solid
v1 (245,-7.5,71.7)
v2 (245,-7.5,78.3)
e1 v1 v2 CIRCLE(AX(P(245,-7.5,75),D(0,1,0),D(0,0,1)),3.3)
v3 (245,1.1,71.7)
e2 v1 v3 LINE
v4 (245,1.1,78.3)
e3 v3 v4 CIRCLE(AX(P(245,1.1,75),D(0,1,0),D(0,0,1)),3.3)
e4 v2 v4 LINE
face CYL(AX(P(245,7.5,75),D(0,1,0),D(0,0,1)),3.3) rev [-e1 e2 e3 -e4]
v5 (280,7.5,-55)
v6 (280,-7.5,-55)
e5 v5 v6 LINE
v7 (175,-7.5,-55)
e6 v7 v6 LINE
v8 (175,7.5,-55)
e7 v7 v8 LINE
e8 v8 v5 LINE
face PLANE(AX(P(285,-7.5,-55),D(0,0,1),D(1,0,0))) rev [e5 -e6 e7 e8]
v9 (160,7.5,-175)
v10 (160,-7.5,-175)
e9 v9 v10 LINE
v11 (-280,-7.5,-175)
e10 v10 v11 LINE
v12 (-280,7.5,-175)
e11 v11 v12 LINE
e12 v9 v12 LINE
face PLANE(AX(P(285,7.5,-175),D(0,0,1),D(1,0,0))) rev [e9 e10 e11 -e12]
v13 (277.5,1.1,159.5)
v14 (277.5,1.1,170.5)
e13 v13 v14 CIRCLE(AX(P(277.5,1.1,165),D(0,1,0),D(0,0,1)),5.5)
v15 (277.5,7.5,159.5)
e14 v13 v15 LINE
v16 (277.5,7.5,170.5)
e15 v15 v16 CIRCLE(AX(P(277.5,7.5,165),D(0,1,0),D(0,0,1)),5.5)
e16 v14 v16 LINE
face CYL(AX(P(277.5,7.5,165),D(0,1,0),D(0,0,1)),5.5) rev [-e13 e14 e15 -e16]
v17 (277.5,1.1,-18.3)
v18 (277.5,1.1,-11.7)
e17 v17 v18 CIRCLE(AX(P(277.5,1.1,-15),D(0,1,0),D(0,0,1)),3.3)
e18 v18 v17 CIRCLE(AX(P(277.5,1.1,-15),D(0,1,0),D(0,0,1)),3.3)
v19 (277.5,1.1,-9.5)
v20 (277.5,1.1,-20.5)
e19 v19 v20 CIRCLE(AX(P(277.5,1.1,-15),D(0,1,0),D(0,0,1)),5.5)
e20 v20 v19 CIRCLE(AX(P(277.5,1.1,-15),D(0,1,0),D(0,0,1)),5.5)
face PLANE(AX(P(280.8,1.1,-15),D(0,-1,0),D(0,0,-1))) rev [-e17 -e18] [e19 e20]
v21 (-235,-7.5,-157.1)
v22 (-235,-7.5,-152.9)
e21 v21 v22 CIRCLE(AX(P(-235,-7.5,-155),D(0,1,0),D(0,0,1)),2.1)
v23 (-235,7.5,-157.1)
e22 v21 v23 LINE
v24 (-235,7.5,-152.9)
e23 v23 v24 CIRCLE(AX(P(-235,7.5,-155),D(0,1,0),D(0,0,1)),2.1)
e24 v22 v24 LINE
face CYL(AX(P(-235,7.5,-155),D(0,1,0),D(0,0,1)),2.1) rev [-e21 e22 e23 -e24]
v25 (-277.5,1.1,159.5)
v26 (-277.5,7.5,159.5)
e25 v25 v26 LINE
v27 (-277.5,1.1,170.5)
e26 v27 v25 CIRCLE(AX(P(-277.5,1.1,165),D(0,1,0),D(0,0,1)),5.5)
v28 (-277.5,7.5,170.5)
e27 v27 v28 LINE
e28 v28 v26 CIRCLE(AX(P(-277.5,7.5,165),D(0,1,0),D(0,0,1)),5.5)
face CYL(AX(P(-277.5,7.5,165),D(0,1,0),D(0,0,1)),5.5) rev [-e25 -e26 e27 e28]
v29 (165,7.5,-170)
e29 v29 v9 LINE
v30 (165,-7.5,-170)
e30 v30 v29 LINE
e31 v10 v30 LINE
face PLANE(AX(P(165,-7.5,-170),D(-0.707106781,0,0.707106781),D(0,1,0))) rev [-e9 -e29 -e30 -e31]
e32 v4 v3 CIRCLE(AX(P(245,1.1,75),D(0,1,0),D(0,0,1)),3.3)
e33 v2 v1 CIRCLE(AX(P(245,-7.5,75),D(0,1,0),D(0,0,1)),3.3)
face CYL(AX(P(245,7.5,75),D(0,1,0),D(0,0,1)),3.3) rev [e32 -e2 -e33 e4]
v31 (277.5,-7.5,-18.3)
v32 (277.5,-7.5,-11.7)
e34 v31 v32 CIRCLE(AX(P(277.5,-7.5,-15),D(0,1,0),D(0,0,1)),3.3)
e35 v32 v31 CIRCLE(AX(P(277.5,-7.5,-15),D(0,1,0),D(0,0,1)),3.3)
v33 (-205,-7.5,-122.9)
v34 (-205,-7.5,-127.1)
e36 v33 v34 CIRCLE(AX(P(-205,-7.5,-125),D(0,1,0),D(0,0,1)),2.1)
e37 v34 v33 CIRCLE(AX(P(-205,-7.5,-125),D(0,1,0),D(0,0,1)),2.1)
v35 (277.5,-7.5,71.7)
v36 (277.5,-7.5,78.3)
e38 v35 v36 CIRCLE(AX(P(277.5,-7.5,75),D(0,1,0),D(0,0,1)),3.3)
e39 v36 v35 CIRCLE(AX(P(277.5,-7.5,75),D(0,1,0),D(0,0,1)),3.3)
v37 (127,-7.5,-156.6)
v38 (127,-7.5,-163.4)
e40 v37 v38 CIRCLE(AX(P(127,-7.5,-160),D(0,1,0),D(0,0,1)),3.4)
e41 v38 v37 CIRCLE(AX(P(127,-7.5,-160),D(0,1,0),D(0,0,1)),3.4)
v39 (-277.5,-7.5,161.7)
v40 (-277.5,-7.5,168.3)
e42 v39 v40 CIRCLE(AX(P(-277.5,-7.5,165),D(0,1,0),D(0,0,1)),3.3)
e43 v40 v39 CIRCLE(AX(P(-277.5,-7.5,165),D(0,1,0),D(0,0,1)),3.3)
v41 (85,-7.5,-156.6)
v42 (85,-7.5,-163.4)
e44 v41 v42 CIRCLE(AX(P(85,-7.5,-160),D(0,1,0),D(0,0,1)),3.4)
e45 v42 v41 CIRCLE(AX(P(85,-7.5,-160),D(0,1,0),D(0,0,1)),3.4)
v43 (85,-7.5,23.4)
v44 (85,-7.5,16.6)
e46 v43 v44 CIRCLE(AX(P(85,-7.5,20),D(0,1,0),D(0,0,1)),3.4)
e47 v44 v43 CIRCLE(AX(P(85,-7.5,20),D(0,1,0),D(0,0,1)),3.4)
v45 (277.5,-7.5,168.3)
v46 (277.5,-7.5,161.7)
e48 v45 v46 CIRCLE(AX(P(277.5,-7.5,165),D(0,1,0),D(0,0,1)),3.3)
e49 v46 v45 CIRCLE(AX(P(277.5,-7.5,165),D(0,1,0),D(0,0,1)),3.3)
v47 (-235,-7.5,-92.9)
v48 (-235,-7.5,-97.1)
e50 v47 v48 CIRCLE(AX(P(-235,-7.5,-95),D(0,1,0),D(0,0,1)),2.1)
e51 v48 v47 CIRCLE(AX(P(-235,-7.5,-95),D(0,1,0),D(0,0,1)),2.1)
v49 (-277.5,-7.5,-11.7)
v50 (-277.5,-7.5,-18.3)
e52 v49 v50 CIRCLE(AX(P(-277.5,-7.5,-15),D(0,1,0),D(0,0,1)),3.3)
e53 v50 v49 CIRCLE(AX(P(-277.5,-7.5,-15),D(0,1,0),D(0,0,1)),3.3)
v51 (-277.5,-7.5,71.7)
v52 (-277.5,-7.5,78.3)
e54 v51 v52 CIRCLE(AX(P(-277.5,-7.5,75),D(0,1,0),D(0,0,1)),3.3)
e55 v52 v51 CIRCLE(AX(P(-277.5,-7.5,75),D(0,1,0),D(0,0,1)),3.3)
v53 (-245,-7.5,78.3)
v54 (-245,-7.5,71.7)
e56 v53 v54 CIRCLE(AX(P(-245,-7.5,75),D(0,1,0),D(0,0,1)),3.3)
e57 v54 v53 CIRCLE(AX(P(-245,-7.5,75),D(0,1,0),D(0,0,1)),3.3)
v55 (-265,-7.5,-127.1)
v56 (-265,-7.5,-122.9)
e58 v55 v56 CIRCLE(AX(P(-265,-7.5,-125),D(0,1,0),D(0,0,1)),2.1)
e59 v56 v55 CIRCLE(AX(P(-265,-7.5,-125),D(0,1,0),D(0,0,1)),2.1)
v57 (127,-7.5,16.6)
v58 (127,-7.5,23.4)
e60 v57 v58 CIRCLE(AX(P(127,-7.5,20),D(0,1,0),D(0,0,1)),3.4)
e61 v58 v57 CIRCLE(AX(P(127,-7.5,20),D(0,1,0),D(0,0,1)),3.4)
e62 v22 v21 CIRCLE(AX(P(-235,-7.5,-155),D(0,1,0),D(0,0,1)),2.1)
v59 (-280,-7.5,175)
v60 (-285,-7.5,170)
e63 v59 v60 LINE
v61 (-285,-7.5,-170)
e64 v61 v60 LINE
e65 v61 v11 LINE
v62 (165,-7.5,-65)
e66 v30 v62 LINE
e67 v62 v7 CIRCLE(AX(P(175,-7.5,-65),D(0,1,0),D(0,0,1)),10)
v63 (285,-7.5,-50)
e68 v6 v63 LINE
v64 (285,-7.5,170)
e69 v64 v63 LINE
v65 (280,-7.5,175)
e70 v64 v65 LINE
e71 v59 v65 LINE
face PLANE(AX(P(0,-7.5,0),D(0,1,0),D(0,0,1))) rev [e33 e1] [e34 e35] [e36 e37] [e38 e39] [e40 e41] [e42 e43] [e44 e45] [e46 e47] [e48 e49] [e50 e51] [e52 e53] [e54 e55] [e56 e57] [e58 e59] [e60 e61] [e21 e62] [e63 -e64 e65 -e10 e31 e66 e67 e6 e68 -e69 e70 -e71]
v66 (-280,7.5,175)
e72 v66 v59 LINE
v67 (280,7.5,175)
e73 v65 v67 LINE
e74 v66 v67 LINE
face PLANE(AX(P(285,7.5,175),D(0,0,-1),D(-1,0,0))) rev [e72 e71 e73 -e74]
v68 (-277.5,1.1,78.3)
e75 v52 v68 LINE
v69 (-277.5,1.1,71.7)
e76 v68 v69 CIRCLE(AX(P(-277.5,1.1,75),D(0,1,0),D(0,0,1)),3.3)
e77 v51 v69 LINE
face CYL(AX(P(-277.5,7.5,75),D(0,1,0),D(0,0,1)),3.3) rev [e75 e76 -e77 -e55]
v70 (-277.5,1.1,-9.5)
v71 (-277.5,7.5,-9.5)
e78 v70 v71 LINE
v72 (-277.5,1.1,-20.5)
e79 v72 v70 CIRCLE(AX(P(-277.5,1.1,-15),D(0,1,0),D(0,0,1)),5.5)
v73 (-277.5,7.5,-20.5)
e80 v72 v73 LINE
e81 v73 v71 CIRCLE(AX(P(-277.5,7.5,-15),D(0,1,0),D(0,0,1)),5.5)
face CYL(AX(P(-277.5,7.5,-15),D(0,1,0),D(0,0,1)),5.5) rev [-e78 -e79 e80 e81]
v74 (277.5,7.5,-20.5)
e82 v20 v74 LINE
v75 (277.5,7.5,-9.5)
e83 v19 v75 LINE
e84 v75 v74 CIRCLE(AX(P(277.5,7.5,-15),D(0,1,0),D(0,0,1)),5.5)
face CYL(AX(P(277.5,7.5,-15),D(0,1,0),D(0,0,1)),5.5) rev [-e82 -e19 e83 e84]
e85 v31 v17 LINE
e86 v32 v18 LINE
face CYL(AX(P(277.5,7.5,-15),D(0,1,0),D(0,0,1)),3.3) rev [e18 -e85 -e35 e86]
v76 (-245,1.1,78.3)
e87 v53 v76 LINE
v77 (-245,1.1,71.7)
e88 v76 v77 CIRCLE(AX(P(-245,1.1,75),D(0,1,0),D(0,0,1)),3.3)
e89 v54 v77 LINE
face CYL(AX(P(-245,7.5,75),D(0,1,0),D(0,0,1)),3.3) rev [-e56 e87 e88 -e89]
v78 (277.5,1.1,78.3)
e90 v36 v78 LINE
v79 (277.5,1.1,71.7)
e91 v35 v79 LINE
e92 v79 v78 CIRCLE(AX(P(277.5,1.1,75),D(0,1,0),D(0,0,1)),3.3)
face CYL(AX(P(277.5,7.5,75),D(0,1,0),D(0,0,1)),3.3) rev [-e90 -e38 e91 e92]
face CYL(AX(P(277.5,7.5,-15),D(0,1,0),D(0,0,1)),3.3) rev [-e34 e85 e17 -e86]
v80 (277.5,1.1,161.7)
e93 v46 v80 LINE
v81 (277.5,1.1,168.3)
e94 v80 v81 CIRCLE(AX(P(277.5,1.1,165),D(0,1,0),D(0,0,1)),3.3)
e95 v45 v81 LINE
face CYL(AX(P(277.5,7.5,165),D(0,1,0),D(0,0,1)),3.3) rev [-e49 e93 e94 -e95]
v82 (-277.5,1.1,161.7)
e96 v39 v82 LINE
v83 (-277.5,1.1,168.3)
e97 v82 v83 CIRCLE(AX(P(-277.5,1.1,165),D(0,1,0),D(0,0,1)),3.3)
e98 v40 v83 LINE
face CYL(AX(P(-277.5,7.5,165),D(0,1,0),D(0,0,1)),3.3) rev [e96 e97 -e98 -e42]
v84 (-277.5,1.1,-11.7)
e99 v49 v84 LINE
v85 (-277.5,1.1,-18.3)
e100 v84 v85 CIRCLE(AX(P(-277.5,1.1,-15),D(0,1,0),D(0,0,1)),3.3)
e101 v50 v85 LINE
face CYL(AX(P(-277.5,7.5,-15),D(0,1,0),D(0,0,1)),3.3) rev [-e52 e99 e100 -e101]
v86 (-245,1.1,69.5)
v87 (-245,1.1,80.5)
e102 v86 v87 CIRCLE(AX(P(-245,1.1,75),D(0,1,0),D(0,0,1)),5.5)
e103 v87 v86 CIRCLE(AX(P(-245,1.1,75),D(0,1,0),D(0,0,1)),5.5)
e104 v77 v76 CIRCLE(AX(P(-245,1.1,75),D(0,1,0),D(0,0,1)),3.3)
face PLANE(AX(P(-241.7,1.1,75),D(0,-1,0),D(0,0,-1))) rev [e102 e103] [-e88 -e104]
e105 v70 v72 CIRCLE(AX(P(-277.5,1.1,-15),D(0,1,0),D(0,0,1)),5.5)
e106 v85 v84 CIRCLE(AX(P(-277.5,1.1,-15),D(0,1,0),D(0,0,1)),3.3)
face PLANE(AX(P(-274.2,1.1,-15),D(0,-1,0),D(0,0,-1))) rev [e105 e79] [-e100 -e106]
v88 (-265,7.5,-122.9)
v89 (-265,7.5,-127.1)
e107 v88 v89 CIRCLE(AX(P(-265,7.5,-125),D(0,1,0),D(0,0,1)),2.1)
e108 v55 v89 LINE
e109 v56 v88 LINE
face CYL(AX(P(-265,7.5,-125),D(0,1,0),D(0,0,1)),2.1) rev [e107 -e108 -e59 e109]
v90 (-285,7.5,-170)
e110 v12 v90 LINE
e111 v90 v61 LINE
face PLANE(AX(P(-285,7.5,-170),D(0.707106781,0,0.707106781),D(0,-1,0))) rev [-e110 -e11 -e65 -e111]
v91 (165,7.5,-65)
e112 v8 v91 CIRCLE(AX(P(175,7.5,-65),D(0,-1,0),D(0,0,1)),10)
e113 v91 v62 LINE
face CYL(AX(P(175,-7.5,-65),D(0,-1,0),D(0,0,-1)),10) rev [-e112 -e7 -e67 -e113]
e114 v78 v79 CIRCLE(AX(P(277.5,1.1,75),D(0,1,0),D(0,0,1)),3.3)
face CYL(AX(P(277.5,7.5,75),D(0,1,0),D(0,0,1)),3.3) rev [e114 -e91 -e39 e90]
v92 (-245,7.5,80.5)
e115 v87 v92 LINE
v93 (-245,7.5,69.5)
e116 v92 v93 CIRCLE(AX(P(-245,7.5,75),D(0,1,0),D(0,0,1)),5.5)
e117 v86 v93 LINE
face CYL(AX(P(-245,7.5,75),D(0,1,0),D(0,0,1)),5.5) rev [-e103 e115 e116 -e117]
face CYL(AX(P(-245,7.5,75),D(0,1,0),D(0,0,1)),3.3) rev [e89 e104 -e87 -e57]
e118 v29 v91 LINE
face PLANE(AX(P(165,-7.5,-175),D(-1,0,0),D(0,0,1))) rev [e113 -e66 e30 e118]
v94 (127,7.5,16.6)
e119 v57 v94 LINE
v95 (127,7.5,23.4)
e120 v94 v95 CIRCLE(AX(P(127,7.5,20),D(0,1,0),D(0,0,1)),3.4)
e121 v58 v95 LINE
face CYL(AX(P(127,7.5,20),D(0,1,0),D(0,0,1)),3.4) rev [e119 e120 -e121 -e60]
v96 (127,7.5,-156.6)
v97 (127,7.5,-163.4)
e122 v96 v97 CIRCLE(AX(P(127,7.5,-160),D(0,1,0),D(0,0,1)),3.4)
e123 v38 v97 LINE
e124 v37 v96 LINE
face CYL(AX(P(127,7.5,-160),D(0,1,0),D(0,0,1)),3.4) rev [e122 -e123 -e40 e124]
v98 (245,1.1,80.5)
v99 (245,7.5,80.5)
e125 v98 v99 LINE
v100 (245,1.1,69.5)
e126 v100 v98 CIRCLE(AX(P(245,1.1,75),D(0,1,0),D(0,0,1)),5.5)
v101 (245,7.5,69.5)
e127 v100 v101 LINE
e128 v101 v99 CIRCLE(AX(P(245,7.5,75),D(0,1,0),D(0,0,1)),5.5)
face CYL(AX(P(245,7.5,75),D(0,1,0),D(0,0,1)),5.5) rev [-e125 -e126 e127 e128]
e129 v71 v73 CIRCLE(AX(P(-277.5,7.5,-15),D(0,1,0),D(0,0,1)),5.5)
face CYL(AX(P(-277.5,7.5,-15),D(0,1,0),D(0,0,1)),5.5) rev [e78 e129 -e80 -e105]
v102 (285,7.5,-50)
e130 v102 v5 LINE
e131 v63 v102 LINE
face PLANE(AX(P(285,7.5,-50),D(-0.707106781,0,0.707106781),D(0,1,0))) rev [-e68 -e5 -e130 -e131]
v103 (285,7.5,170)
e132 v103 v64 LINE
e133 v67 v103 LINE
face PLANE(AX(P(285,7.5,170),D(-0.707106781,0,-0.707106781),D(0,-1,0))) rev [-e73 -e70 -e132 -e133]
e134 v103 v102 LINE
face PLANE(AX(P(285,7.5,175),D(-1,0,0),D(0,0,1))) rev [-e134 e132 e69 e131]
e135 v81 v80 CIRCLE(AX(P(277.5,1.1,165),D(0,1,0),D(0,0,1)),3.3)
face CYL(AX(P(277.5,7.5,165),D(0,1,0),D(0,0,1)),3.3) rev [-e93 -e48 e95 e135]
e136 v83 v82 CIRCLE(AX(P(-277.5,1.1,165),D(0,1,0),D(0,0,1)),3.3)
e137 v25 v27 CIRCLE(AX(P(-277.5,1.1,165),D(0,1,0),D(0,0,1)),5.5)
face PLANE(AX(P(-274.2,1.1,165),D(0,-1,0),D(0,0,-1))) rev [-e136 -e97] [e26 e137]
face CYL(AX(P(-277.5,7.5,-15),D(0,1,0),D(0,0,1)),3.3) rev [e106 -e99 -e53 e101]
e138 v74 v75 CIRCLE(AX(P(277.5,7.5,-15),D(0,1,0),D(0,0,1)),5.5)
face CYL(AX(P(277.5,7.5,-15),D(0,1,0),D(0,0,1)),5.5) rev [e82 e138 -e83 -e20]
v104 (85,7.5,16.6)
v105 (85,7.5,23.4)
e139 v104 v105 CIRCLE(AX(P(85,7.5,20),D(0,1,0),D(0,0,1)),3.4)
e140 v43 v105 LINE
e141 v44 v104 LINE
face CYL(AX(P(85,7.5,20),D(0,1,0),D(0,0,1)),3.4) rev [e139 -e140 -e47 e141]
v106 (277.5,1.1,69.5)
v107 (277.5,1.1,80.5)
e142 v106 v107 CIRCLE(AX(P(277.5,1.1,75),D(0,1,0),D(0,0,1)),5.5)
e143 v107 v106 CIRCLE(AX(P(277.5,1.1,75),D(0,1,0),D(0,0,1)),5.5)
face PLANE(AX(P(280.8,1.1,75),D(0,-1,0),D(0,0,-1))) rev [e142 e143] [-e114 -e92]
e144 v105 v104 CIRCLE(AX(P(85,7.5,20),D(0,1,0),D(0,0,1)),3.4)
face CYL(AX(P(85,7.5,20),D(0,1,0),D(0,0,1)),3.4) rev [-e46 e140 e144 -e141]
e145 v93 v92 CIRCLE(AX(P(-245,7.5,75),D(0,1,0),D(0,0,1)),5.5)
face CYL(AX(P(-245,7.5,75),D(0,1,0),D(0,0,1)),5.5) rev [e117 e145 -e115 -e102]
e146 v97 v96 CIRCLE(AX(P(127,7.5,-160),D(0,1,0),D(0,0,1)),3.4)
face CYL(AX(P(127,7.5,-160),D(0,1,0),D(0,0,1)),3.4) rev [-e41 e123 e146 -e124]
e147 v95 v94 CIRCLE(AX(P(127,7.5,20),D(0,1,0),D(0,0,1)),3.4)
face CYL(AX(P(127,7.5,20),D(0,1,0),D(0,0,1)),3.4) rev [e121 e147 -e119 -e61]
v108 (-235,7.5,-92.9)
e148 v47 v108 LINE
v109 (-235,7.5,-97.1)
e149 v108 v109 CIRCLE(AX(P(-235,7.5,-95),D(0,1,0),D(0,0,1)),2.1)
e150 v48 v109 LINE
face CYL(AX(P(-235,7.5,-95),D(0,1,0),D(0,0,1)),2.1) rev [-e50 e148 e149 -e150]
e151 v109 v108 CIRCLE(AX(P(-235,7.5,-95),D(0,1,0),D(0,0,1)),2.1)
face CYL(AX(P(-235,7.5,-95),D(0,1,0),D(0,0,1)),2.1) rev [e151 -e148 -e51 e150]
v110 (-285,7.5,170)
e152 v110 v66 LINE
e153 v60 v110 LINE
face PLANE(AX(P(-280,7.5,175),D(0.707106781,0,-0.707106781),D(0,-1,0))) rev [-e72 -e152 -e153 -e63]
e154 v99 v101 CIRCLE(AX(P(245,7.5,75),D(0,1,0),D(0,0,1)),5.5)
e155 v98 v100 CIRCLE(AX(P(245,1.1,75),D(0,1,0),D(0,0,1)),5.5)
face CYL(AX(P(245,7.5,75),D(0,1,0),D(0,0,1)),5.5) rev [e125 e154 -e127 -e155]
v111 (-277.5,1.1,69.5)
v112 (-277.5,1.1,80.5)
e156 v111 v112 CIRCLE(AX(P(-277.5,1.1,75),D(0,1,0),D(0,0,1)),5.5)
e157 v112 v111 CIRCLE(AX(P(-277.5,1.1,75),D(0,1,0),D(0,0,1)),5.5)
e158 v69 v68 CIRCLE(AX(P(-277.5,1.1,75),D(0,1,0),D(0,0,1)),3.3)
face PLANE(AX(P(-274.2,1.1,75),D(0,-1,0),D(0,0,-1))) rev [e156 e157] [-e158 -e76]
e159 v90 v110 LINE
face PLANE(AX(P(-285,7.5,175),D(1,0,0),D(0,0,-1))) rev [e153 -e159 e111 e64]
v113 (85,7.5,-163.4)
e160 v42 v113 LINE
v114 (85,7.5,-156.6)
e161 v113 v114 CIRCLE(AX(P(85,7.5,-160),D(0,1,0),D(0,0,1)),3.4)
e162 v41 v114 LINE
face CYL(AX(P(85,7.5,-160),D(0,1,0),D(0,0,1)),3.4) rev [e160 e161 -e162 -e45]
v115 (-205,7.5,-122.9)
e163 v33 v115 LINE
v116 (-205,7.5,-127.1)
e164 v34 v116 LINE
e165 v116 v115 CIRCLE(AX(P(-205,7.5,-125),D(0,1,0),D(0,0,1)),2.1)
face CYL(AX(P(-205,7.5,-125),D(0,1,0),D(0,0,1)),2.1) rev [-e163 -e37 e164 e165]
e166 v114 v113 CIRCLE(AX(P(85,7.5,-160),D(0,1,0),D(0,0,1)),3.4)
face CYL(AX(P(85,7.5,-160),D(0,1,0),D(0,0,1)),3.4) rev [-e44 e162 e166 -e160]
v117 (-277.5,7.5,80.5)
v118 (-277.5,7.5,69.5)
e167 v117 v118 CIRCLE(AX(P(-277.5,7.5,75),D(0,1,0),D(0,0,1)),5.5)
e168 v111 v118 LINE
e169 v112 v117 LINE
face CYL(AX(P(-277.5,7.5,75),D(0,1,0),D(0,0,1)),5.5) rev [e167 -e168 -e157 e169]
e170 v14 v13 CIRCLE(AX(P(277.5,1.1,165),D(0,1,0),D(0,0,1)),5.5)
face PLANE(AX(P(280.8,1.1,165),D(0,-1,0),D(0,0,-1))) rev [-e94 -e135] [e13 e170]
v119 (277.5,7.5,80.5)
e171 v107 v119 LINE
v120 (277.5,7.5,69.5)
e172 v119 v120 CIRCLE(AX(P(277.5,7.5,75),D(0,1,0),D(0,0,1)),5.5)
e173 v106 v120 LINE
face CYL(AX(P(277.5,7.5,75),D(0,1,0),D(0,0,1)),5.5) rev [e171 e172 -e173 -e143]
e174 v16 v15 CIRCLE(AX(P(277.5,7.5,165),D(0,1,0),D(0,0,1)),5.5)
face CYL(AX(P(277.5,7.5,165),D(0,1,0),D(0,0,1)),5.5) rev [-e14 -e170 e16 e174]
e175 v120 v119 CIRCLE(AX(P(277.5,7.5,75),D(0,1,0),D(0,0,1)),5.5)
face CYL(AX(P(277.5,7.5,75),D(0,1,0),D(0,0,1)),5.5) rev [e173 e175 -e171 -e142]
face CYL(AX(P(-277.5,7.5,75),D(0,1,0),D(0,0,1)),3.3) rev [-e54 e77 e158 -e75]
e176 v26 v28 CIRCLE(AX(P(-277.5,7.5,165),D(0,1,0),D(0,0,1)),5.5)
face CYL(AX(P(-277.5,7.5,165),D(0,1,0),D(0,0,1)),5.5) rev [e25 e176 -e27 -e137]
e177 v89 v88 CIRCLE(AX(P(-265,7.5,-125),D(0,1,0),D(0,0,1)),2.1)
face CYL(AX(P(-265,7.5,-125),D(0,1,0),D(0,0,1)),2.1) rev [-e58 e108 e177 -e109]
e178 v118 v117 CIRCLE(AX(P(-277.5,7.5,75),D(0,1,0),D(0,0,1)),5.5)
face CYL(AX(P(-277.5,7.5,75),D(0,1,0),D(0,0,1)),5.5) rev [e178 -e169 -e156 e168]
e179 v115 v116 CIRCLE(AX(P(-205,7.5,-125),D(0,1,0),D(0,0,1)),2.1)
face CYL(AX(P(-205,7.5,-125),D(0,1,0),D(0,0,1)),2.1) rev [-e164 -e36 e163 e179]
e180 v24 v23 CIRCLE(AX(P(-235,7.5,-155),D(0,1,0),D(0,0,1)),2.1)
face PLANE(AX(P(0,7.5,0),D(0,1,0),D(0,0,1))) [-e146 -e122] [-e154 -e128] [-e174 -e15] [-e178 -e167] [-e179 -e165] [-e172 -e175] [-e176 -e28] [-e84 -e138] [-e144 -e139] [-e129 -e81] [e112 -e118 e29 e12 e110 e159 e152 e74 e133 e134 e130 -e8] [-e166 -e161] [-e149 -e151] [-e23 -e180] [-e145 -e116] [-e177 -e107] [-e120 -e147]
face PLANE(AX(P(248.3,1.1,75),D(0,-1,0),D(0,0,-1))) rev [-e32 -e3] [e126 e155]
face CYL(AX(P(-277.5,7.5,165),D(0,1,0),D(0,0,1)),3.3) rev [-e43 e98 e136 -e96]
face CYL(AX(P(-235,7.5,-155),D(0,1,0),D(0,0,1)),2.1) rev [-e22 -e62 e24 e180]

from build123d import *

# Parameters (mm, degrees)
SKETCH_1_W                   = 570
SKETCH_1_H                   = 350
EXTRUDE_1_DEPTH              = 7.5
CHAMFER_1_SIZE               = 5
HOLE_WIZARD_M5_1_D           = 4.2
HOLE_WIZARD_M8_1_D           = 6.8
HOLE_WIZARD_M6_1_D           = 6.6
HOLE_WIZARD_M6_1_DEPTH       = 17
HOLE_WIZARD_M6_1_CBORE_D     = 11
HOLE_WIZARD_M6_1_CBORE_DEPTH = 6.4
HOLE_WIZARD_M6_1_TIP         = 1.982840043
HOLE_WIZARD_M6_2_D           = 6.6
HOLE_WIZARD_M6_2_DEPTH       = 17
HOLE_WIZARD_M6_2_CBORE_D     = 11
HOLE_WIZARD_M6_2_CBORE_DEPTH = 6.4
HOLE_WIZARD_M6_2_TIP         = 1.982840043
SKETCH_10_W                  = 120
SKETCH_10_H                  = 120
CUT_EXTRUDE_1_DEPTH          = 335.776044543
FILLET_1_R                   = 10
CHAMFER_2_SIZE               = 5


with BuildPart() as part:
    # 草图1 → 凸台-拉伸1 (new, symmetric)
    with BuildSketch(Plane(origin=(0, 0, 0), x_dir=(1, 0, 0), z_dir=(0, 1, 0))):
        Rectangle(SKETCH_1_W, SKETCH_1_H)
    extrude(amount=EXTRUDE_1_DEPTH, both=True)

    # 倒角1
    chamfer_1_edges = [part.edges().sort_by_distance(p)[0] for p in [
        (-285, 0, -175),
        (285, 0, -175),
        (285, 0, 175),
        (-285, 0, 175),
    ]]
    chamfer(chamfer_1_edges, length=CHAMFER_1_SIZE)

    # M5 螺纹孔1 (through all)
    with Locations(Plane(origin=(0, 7.5, 0), x_dir=(1, 0, 0), z_dir=(0, 1, 0))):
        with Locations((-265, 125), (-235, 95), (-235, 155), (-205, 125)):
            Hole(HOLE_WIZARD_M5_1_D / 2)

    # M8 螺纹孔1 (through all)
    with Locations(Plane(origin=(0, 7.5, 0), x_dir=(1, 0, 0), z_dir=(0, 1, 0))):
        with Locations((85, -20), (127, -20), (127, 160), (85, 160)):
            Hole(HOLE_WIZARD_M8_1_D / 2)

    # M6 六角凹头螺钉的柱形沉头孔1
    with Locations(Plane(origin=(0, 7.5, 0), x_dir=(1, 0, 0), z_dir=(0, 1, 0))):
        with Locations((-277.5, 15), (-277.5, -165), (277.5, 15), (277.5, -165), (-277.5, -75), (277.5, -75)):
            CounterBoreHole(HOLE_WIZARD_M6_1_D / 2, HOLE_WIZARD_M6_1_CBORE_D / 2, HOLE_WIZARD_M6_1_CBORE_DEPTH, depth=HOLE_WIZARD_M6_1_DEPTH)
            with Locations((0, 0, -(HOLE_WIZARD_M6_1_DEPTH + HOLE_WIZARD_M6_1_TIP / 2))):  # 118° drill point
                Cone(0, HOLE_WIZARD_M6_1_D / 2, HOLE_WIZARD_M6_1_TIP, mode=Mode.SUBTRACT)

    # M6 六角凹头螺钉的柱形沉头孔2
    with Locations(Plane(origin=(0, 7.5, 0), x_dir=(1, 0, 0), z_dir=(0, 1, 0))):
        with Locations((-245, -75), (245, -75)):
            CounterBoreHole(HOLE_WIZARD_M6_2_D / 2, HOLE_WIZARD_M6_2_CBORE_D / 2, HOLE_WIZARD_M6_2_CBORE_DEPTH, depth=HOLE_WIZARD_M6_2_DEPTH)
            with Locations((0, 0, -(HOLE_WIZARD_M6_2_DEPTH + HOLE_WIZARD_M6_2_TIP / 2))):  # 118° drill point
                Cone(0, HOLE_WIZARD_M6_2_D / 2, HOLE_WIZARD_M6_2_TIP, mode=Mode.SUBTRACT)

    # 草图10 → 切除-拉伸1 (cut, through all)
    with BuildSketch(Plane(origin=(0, 7.5, 0), x_dir=(1, 0, 0), z_dir=(0, 1, 0))):
        with Locations((225, 115)):
            Rectangle(SKETCH_10_W, SKETCH_10_H)
    extrude(amount=-CUT_EXTRUDE_1_DEPTH, mode=Mode.SUBTRACT)

    # 圆角1
    fillet_1_edges = [part.edges().sort_by_distance(p)[0] for p in [
        (165, 0, -55),
    ]]
    fillet(fillet_1_edges, radius=FILLET_1_R)

    # 倒角2
    chamfer_2_edges = [part.edges().sort_by_distance(p)[0] for p in [
        (285, 0, -55),
        (165, 0, -175),
    ]]
    chamfer(chamfer_2_edges, length=CHAMFER_2_SIZE)


solid = part.part
